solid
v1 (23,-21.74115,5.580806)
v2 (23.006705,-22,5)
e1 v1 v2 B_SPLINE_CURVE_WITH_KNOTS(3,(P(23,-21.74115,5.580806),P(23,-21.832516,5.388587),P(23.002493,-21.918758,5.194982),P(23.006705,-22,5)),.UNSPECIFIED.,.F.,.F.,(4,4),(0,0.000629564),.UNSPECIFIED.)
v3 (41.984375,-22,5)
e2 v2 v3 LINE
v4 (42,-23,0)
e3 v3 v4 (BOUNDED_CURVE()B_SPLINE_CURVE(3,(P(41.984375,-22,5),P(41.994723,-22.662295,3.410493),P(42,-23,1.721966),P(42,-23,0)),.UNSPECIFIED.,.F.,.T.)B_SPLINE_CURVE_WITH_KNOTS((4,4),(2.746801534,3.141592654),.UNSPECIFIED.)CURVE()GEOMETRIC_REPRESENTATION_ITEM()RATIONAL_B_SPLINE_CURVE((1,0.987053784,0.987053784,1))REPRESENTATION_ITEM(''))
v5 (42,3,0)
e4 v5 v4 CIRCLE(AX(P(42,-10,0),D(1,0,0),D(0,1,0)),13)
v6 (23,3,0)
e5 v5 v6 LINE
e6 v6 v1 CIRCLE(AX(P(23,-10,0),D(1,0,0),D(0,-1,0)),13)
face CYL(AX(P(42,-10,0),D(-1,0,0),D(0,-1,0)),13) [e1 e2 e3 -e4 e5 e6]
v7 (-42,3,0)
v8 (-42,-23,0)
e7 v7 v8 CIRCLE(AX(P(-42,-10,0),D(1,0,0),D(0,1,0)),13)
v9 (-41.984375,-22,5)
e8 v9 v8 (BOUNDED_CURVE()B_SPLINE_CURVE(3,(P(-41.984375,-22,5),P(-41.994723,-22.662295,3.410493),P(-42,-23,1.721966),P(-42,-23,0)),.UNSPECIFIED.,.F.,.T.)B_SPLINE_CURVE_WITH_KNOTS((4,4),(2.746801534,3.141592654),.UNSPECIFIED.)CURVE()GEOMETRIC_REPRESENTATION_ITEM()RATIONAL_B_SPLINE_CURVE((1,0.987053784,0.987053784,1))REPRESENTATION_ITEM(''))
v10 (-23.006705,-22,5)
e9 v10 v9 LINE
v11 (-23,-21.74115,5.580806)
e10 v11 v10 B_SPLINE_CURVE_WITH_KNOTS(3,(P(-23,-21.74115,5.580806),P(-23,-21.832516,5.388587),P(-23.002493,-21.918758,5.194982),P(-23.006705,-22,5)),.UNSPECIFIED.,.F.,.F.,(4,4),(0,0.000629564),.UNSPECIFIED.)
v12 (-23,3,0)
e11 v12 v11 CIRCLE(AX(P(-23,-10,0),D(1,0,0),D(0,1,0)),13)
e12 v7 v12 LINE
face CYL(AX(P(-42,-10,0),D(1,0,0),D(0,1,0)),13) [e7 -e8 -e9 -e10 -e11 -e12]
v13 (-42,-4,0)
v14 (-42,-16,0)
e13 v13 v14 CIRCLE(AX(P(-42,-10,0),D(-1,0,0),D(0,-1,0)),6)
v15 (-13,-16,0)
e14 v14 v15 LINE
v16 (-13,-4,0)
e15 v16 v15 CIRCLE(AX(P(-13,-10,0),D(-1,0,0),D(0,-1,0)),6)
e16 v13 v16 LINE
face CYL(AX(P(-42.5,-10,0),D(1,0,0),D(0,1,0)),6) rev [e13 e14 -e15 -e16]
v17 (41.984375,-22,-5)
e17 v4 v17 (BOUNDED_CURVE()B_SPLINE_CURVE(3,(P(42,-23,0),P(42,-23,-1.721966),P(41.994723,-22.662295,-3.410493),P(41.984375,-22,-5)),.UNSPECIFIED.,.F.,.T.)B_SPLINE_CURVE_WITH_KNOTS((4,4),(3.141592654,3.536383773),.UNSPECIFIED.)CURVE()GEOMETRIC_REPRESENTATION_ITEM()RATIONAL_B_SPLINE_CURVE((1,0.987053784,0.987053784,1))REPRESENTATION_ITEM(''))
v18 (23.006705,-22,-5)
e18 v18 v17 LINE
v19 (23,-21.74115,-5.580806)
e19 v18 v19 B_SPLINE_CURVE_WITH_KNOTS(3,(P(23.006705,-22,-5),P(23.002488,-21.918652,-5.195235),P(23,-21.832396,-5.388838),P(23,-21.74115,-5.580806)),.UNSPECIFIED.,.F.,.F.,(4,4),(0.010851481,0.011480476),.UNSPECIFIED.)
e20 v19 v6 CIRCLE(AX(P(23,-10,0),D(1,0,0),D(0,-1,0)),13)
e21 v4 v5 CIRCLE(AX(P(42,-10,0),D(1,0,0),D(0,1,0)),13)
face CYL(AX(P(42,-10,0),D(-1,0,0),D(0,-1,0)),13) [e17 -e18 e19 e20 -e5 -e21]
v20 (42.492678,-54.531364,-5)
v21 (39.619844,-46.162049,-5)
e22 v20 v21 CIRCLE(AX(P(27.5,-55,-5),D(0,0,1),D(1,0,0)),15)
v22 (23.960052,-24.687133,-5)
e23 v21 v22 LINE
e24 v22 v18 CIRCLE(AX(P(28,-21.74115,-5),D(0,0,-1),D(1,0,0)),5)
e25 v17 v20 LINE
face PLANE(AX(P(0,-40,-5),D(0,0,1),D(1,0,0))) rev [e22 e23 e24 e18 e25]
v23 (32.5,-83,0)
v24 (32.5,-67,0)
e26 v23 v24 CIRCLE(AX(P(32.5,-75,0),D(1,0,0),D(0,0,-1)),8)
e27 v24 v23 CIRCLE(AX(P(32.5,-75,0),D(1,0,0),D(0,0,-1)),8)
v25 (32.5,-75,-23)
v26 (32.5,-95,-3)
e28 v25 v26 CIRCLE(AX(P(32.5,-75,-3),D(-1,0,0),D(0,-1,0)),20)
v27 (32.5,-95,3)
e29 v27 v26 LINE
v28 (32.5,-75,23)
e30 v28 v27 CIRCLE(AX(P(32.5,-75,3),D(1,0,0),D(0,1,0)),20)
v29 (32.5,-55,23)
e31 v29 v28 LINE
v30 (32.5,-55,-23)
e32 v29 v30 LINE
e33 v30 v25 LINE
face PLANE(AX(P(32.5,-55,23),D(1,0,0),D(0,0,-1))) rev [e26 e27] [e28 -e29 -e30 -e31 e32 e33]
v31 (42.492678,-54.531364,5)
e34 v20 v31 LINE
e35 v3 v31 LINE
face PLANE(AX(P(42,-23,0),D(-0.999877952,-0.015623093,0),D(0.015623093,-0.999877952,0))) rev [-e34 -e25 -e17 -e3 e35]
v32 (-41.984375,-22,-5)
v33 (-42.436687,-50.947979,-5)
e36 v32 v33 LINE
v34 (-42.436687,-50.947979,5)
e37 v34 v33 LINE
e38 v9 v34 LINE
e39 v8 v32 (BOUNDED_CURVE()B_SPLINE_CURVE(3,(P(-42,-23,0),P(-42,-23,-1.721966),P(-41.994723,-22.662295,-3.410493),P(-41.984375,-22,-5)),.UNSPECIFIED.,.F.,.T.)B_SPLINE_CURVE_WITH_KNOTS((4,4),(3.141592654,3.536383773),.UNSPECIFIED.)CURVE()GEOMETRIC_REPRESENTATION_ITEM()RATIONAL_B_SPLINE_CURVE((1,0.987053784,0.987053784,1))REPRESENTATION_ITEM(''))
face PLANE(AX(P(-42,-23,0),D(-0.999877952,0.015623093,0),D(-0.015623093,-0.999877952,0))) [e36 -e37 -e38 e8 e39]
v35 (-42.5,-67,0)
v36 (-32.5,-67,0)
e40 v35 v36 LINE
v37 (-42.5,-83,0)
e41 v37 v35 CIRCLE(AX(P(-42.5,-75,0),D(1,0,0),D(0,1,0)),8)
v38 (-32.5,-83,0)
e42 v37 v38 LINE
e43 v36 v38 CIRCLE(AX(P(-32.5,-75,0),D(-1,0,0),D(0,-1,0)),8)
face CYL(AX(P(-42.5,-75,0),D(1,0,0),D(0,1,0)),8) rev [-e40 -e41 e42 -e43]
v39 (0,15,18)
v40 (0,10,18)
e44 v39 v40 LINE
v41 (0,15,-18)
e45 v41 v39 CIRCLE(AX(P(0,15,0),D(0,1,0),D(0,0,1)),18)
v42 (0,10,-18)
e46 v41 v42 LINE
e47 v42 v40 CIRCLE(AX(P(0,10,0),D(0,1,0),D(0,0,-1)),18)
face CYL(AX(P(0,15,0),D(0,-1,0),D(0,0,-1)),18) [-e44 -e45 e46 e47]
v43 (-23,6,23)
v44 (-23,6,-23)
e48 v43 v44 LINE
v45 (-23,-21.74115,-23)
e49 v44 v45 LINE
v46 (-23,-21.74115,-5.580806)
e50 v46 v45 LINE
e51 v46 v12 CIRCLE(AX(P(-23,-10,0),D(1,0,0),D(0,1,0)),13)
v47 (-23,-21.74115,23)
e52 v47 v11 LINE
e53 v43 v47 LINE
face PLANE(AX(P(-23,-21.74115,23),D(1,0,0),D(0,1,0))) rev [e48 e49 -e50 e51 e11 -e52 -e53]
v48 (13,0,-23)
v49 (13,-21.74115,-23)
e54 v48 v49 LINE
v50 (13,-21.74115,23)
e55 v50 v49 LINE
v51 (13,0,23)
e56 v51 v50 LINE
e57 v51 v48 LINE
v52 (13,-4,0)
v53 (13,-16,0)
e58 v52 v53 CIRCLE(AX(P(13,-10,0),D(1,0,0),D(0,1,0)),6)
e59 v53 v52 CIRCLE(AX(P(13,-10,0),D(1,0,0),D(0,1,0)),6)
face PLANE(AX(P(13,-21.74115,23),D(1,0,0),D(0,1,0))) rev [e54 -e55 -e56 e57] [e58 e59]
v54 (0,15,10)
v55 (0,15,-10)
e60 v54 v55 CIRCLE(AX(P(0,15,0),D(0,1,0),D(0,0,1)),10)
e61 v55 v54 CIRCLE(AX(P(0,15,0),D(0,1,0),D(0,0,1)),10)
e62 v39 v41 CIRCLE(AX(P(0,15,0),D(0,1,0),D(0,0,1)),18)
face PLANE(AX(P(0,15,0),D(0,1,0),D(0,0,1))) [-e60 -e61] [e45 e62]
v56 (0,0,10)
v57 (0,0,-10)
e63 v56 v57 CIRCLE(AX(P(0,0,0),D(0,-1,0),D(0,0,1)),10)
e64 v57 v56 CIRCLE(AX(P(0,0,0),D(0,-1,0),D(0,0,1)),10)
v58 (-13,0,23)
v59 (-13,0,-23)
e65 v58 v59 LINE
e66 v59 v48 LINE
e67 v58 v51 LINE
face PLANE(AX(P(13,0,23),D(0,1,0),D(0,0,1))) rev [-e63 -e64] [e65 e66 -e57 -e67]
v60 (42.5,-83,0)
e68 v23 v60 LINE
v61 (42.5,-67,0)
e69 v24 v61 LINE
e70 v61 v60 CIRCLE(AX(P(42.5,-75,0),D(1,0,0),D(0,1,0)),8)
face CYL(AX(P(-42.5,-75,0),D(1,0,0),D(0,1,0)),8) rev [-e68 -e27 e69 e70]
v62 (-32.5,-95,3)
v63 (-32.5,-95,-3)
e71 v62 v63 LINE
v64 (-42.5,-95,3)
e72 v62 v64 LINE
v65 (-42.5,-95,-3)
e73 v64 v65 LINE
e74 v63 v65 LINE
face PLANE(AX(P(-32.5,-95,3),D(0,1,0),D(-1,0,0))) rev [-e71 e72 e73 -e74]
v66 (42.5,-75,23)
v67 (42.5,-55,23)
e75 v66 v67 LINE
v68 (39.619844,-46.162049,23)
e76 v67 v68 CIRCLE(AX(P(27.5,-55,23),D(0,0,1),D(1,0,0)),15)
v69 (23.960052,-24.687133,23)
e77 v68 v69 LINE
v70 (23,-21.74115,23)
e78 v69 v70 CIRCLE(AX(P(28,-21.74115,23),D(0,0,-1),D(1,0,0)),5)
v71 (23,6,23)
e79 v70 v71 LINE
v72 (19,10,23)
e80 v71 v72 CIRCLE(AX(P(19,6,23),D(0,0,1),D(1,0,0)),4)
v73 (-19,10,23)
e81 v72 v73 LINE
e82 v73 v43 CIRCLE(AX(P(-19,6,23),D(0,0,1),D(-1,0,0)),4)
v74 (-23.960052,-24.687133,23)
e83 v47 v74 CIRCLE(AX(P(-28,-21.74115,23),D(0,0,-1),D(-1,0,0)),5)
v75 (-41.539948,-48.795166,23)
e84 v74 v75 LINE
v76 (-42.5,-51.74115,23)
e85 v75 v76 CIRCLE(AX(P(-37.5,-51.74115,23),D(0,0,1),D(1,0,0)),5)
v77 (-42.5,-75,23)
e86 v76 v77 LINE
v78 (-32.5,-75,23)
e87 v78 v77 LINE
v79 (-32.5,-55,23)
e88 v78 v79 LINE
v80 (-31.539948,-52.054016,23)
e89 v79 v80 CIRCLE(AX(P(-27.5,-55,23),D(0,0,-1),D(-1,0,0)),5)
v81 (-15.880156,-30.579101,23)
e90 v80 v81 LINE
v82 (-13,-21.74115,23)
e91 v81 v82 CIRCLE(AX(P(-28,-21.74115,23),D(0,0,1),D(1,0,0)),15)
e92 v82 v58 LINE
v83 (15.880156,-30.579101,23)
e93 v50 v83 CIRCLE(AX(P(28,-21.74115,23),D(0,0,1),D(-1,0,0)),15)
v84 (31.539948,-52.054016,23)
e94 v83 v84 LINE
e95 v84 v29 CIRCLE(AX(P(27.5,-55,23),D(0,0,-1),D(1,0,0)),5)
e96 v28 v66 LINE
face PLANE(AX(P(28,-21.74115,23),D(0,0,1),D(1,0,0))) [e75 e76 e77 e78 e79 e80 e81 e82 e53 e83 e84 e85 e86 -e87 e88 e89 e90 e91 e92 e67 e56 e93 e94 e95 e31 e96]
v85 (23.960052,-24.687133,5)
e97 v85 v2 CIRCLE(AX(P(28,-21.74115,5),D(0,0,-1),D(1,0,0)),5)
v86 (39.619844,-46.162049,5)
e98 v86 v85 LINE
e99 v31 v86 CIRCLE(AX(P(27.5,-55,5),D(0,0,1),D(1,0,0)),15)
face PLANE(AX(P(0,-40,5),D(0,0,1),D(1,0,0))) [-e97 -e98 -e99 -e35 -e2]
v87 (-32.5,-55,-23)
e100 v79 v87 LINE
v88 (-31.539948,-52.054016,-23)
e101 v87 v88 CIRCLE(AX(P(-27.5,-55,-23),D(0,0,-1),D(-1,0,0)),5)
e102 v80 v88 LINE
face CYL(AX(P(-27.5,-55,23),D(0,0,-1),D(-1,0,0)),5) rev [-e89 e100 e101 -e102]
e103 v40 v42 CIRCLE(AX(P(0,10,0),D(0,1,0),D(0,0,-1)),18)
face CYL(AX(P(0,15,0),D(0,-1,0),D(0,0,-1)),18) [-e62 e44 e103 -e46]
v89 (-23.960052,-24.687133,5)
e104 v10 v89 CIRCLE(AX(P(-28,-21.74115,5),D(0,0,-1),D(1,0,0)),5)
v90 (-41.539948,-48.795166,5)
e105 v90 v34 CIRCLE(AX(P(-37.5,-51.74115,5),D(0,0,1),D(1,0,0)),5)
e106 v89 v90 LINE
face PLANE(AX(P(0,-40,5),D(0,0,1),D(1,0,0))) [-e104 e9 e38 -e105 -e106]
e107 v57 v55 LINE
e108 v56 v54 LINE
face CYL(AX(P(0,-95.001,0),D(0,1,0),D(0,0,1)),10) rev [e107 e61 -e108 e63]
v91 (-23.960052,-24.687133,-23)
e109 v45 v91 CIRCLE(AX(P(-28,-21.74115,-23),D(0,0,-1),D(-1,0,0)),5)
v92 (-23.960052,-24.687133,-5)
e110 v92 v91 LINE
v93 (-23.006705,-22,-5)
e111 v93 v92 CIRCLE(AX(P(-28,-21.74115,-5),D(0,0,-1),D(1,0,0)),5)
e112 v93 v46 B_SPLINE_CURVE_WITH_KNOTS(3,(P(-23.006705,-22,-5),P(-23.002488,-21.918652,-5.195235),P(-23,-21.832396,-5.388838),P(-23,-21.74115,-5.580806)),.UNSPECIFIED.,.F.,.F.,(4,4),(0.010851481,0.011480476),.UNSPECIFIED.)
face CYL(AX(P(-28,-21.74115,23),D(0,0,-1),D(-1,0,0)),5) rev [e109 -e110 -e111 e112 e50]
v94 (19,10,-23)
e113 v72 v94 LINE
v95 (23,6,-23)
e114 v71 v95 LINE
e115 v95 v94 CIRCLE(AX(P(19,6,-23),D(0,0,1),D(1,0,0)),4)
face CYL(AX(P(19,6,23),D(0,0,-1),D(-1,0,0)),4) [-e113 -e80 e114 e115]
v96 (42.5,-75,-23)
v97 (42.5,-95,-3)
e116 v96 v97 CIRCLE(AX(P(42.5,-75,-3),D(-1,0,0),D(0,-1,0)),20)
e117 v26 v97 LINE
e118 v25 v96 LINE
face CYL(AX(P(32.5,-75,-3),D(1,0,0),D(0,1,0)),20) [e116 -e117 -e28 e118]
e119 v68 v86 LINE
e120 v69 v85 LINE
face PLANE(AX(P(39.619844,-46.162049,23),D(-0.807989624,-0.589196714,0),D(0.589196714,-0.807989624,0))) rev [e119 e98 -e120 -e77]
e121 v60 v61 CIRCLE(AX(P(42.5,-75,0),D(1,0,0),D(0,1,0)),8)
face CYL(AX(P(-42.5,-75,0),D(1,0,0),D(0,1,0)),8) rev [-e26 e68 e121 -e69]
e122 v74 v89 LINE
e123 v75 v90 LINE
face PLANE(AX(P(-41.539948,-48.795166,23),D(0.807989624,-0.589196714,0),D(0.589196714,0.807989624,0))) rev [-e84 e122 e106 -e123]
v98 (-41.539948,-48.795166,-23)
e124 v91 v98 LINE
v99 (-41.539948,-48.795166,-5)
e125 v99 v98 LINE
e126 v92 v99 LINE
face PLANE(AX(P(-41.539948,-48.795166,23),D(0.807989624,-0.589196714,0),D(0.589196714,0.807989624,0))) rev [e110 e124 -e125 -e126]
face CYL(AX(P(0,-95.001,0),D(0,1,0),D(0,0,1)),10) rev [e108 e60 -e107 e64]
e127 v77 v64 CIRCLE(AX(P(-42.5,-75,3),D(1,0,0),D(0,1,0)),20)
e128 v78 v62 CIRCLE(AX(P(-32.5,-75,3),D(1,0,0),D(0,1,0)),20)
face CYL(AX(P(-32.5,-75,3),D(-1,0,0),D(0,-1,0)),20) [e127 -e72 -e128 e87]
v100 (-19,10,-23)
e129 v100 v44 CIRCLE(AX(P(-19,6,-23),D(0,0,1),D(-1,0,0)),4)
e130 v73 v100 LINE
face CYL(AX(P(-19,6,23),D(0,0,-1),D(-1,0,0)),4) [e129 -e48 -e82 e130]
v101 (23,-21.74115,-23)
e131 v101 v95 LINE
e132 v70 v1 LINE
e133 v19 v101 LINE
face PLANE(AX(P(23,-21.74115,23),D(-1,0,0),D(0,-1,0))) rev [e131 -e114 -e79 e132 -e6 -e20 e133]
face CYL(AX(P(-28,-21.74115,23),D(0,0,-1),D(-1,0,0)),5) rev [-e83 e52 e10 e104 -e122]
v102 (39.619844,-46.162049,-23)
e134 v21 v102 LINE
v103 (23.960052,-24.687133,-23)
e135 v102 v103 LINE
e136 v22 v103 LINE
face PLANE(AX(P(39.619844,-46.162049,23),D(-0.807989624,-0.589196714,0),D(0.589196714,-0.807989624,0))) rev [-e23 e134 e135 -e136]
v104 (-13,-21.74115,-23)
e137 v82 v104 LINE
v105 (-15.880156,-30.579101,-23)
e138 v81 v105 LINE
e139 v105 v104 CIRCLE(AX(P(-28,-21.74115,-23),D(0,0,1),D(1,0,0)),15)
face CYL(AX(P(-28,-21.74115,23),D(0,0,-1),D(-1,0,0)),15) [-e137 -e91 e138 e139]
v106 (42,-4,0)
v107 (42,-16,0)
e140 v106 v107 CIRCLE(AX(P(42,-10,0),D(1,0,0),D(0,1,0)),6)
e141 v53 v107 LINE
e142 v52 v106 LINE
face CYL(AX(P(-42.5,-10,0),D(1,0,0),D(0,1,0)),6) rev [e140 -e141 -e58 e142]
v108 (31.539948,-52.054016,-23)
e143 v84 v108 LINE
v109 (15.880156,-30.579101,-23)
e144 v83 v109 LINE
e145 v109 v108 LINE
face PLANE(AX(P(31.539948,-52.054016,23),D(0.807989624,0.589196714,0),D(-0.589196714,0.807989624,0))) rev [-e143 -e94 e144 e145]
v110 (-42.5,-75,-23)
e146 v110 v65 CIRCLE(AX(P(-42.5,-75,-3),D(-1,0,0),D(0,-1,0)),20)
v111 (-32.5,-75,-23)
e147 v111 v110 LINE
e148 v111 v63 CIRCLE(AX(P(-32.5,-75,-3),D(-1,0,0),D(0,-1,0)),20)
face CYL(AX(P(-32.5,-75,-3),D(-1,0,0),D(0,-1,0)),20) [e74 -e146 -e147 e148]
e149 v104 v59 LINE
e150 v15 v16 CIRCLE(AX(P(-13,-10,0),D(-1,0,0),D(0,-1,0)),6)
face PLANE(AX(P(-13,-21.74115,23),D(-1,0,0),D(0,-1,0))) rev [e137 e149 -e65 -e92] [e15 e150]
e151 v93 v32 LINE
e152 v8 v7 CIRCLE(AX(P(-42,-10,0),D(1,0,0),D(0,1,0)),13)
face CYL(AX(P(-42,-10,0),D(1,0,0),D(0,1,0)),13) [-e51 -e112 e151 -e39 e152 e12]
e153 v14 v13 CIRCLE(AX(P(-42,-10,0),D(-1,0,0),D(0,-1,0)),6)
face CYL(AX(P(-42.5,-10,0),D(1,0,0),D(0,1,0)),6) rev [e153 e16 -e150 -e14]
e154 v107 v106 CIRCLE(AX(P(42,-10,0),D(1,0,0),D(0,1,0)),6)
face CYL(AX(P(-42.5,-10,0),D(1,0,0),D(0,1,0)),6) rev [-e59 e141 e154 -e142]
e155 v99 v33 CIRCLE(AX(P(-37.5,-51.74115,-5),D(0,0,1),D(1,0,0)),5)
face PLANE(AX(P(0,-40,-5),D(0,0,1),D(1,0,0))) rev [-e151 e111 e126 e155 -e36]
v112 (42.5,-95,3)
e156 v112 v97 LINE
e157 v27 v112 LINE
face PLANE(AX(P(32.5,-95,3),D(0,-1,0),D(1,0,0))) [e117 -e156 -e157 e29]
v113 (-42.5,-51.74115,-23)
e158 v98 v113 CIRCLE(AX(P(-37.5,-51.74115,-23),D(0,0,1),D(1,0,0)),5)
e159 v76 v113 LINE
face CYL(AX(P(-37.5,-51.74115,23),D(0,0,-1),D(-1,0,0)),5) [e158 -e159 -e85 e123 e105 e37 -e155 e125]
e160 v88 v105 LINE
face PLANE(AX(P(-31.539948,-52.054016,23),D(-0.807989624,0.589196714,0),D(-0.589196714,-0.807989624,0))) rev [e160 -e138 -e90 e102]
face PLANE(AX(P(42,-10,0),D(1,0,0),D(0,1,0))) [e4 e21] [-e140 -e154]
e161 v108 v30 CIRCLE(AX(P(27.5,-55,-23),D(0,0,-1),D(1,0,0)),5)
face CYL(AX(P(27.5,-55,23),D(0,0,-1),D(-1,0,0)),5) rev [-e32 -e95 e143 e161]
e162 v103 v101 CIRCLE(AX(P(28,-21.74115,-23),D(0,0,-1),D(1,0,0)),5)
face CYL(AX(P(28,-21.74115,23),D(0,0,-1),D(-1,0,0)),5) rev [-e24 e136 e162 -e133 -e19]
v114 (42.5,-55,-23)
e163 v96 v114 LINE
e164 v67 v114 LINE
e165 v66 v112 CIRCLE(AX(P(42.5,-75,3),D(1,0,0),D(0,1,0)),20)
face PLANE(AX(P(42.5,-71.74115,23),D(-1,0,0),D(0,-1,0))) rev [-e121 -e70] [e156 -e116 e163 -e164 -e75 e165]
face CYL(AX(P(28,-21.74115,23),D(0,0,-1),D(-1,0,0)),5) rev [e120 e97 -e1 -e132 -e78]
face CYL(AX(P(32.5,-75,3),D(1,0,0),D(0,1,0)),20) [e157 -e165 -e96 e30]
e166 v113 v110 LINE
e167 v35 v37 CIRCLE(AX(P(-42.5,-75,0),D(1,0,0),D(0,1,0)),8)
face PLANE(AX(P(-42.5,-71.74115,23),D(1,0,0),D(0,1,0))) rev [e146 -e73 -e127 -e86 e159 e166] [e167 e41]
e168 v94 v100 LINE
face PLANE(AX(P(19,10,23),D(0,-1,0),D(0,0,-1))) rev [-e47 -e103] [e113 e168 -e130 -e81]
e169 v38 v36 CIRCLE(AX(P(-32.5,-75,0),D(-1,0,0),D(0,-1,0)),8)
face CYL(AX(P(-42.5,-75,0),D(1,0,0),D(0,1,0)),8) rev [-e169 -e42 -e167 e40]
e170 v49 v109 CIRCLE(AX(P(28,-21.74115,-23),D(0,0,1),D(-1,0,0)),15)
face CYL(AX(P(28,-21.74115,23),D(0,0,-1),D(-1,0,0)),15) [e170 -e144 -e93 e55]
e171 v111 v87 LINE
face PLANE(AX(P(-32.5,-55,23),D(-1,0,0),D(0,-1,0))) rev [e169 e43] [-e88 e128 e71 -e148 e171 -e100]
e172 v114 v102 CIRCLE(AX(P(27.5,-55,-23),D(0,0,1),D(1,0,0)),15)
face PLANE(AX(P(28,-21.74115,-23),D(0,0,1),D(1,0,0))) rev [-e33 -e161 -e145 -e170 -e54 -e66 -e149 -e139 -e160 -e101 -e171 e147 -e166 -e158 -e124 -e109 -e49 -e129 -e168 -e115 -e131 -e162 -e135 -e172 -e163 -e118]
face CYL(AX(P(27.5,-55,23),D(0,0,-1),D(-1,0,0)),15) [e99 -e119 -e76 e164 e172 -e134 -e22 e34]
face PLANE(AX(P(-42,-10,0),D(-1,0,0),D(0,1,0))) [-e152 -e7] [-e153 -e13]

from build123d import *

# Parameters (mm, degrees)
YOKE_BODY_DEPTH           = 23
TOP_BLOCK_DEPTH           = 10
TOP_BORE_SKETCH_R         = 8
TOP_BORE_16_DEPTH         = 130.533779378
TOP_COLLAR_SKETCH_R       = 18
TOP_COLLAR_36_DEPTH       = 5
COLLAR_BORE_20_REACH      = 122.147
COLLAR_BORE_SKETCH_R      = 10
SIDE_PIVOT_BOSS_SKETCH_R  = 13
SIDE_PIVOT_BOSS_26_DEPTH  = 19
SIDE_PIVOT_BORE_SKETCH_R  = 6
SIDE_PIVOT_BORE_12_DEPTH  = 130.206230518
SUPPORT_RIB_REACH         = 108.584
SUPPORT_RIB_SKETCH_WALL_W = 247.172853136
SUPPORT_RIB_SKETCH_WALL_H = 10


with BuildPart() as part:
    # Yoke Profile Sketch → Yoke Body (new, symmetric)
    with BuildSketch(Plane.XY):
        with BuildLine():
            Line((19, 10), (-19, 10))
            ThreePointArc((-19, 10), (-21.828427125, 8.828427125), (-23, 6))
            Line((-23, 6), (-23, -21.741149913))
            ThreePointArc((-23, -21.741149913), (-23.246067912, -23.290385113), (-23.960051881, -24.687133484))
            Line((-23.960051881, -24.687133484), (-41.539948119, -48.795166343))
            ThreePointArc((-41.539948119, -48.795166343), (-42.253932088, -50.191914714), (-42.5, -51.741149913))
            Line((-42.5, -51.741149913), (-42.5, -71.741149913))
            Line((-42.5, -71.741149913), (-32.5, -71.741149913))
            Line((-32.5, -71.741149913), (-32.5, -55))
            ThreePointArc((-32.5, -55), (-32.253932088, -53.4507648), (-31.539948119, -52.054016429))
            Line((-31.539948119, -52.054016429), (-15.880155644, -30.579100626))
            ThreePointArc((-15.880155644, -30.579100626), (-13.738203736, -26.388855512), (-13, -21.741149913))
            Line((-13, -21.741149913), (-13, 0))
            Line((-13, 0), (13, 0))
            Line((13, 0), (13, -21.741149913))
            ThreePointArc((13, -21.741149913), (13.738203736, -26.388855512), (15.880155644, -30.579100626))
            Line((15.880155644, -30.579100626), (31.539948119, -52.054016429))
            ThreePointArc((31.539948119, -52.054016429), (32.253932088, -53.4507648), (32.5, -55))
            Line((32.5, -55), (32.5, -71.741149913))
            Line((32.5, -71.741149913), (42.5, -71.741149913))
            Line((42.5, -71.741149913), (42.5, -55))
            ThreePointArc((42.5, -55), (41.761796264, -50.352294401), (39.619844356, -46.162049287))
            Line((39.619844356, -46.162049287), (23.960051881, -24.687133484))
            ThreePointArc((23.960051881, -24.687133484), (23.246067912, -23.290385113), (23, -21.741149913))
            Line((23, -21.741149913), (23, 6))
            ThreePointArc((23, 6), (21.828427125, 8.828427125), (19, 10))
        make_face()
    extrude(amount=YOKE_BODY_DEPTH, both=True)

    # Top Block Sketch → Top Block (add)
    with BuildSketch(Plane(origin=(42.5, 0, 0), x_dir=(0, 0, -1), z_dir=(1, 0, 0))):
        with BuildLine():
            Line((-3, -95), (3, -95))
            ThreePointArc((3, -95), (17.142135624, -89.142135624), (23, -75))
            Line((23, -75), (23, -71.741149913))
            Line((23, -71.741149913), (-23, -71.741149913))
            Line((-23, -71.741149913), (-23, -75))
            ThreePointArc((-23, -75), (-17.142135624, -89.142135624), (-3, -95))
        make_face()
    top_block = extrude(amount=-TOP_BLOCK_DEPTH)

    # Top Block Mirror: Top Block across plane
    add(top_block.mirror(Plane(origin=(0, 0, 0), x_dir=(0, 0, 1), z_dir=(1, 0, 0))))

    # Top Bore Sketch → Top Bore Ø16 (cut, through all)
    with BuildSketch(Plane(origin=(42.5, 0, 0), x_dir=(0, 0, -1), z_dir=(1, 0, 0))):
        with Locations(Location((0, -75, 0), (0, 0, 90))):
            Circle(TOP_BORE_SKETCH_R)
    extrude(amount=-TOP_BORE_16_DEPTH, mode=Mode.SUBTRACT)

    # Top Collar Sketch → Top Collar Ø36 (add)
    with BuildSketch(Plane(origin=(0, 10, 0), x_dir=(1, 0, 0), z_dir=(0, 1, 0))):
        with Locations(Location((0, 0, 0), (0, 0, 90))):
            Circle(TOP_COLLAR_SKETCH_R)
    extrude(amount=TOP_COLLAR_36_DEPTH)

    # Collar Bore Sketch → Collar Bore Ø20 (cut, up to next)
    with BuildSketch(Plane(origin=(0, 15, 0), x_dir=(1, 0, 0), z_dir=(0, 1, 0)), mode=Mode.PRIVATE) as collar_bore_20_sk1:
        with Locations(Location((0, 0, 0), (0, 0, 270))):
            Circle(COLLAR_BORE_SKETCH_R)
    collar_bore_20_tool1 = extrude(collar_bore_20_sk1.sketch, amount=-COLLAR_BORE_20_REACH, mode=Mode.PRIVATE) & part.part
    add(collar_bore_20_tool1.solids().sort_by_distance((0, 15, 0))[0], mode=Mode.SUBTRACT)

    # Side Pivot Boss Sketch → Side Pivot Boss Ø26 (add)
    with BuildSketch(Plane(origin=(23, 0, 0), x_dir=(0, 0, -1), z_dir=(1, 0, 0))):
        with Locations(Location((0, -10, 0), (0, 0, 295.42268723))):
            Circle(SIDE_PIVOT_BOSS_SKETCH_R)
    side_pivot_boss_26 = extrude(amount=SIDE_PIVOT_BOSS_26_DEPTH)

    # Side Pivot Boss Mirror: Side Pivot Boss Ø26 across plane
    add(side_pivot_boss_26.mirror(Plane(origin=(0, 0, 0), x_dir=(0, 0, 1), z_dir=(1, 0, 0))))

    # Side Pivot Bore Sketch → Side Pivot Bore Ø12 (cut, through all)
    with BuildSketch(Plane(origin=(42, 0, 0), x_dir=(0, 0, -1), z_dir=(1, 0, 0))):
        with Locations(Location((0, -10, 0), (0, 0, 270))):
            Circle(SIDE_PIVOT_BORE_SKETCH_R)
    extrude(amount=-SIDE_PIVOT_BORE_12_DEPTH, mode=Mode.SUBTRACT)

    # Support Rib Sketch wall → Support Rib (add, up to next)
    with BuildSketch(Plane(origin=(42.25, -39, 0), x_dir=(0.015623093001, -0.999877952035, 0), z_dir=(0.999877952035, 0.015623093001, 0)), mode=Mode.PRIVATE) as support_rib_sk1:
        Rectangle(SUPPORT_RIB_SKETCH_WALL_W, SUPPORT_RIB_SKETCH_WALL_H)
    support_rib_tool1 = extrude(support_rib_sk1.sketch, amount=-SUPPORT_RIB_REACH, mode=Mode.PRIVATE) - part.part
    support_rib = support_rib_tool1.solids().sort_by_distance((42.25, -39, 0))[0]
    add(support_rib)

    # Support Rib Mirror: Support Rib across plane
    add(support_rib.mirror(Plane(origin=(0, 0, 0), x_dir=(0, 0, 1), z_dir=(1, 0, 0))))


solid = part.part
